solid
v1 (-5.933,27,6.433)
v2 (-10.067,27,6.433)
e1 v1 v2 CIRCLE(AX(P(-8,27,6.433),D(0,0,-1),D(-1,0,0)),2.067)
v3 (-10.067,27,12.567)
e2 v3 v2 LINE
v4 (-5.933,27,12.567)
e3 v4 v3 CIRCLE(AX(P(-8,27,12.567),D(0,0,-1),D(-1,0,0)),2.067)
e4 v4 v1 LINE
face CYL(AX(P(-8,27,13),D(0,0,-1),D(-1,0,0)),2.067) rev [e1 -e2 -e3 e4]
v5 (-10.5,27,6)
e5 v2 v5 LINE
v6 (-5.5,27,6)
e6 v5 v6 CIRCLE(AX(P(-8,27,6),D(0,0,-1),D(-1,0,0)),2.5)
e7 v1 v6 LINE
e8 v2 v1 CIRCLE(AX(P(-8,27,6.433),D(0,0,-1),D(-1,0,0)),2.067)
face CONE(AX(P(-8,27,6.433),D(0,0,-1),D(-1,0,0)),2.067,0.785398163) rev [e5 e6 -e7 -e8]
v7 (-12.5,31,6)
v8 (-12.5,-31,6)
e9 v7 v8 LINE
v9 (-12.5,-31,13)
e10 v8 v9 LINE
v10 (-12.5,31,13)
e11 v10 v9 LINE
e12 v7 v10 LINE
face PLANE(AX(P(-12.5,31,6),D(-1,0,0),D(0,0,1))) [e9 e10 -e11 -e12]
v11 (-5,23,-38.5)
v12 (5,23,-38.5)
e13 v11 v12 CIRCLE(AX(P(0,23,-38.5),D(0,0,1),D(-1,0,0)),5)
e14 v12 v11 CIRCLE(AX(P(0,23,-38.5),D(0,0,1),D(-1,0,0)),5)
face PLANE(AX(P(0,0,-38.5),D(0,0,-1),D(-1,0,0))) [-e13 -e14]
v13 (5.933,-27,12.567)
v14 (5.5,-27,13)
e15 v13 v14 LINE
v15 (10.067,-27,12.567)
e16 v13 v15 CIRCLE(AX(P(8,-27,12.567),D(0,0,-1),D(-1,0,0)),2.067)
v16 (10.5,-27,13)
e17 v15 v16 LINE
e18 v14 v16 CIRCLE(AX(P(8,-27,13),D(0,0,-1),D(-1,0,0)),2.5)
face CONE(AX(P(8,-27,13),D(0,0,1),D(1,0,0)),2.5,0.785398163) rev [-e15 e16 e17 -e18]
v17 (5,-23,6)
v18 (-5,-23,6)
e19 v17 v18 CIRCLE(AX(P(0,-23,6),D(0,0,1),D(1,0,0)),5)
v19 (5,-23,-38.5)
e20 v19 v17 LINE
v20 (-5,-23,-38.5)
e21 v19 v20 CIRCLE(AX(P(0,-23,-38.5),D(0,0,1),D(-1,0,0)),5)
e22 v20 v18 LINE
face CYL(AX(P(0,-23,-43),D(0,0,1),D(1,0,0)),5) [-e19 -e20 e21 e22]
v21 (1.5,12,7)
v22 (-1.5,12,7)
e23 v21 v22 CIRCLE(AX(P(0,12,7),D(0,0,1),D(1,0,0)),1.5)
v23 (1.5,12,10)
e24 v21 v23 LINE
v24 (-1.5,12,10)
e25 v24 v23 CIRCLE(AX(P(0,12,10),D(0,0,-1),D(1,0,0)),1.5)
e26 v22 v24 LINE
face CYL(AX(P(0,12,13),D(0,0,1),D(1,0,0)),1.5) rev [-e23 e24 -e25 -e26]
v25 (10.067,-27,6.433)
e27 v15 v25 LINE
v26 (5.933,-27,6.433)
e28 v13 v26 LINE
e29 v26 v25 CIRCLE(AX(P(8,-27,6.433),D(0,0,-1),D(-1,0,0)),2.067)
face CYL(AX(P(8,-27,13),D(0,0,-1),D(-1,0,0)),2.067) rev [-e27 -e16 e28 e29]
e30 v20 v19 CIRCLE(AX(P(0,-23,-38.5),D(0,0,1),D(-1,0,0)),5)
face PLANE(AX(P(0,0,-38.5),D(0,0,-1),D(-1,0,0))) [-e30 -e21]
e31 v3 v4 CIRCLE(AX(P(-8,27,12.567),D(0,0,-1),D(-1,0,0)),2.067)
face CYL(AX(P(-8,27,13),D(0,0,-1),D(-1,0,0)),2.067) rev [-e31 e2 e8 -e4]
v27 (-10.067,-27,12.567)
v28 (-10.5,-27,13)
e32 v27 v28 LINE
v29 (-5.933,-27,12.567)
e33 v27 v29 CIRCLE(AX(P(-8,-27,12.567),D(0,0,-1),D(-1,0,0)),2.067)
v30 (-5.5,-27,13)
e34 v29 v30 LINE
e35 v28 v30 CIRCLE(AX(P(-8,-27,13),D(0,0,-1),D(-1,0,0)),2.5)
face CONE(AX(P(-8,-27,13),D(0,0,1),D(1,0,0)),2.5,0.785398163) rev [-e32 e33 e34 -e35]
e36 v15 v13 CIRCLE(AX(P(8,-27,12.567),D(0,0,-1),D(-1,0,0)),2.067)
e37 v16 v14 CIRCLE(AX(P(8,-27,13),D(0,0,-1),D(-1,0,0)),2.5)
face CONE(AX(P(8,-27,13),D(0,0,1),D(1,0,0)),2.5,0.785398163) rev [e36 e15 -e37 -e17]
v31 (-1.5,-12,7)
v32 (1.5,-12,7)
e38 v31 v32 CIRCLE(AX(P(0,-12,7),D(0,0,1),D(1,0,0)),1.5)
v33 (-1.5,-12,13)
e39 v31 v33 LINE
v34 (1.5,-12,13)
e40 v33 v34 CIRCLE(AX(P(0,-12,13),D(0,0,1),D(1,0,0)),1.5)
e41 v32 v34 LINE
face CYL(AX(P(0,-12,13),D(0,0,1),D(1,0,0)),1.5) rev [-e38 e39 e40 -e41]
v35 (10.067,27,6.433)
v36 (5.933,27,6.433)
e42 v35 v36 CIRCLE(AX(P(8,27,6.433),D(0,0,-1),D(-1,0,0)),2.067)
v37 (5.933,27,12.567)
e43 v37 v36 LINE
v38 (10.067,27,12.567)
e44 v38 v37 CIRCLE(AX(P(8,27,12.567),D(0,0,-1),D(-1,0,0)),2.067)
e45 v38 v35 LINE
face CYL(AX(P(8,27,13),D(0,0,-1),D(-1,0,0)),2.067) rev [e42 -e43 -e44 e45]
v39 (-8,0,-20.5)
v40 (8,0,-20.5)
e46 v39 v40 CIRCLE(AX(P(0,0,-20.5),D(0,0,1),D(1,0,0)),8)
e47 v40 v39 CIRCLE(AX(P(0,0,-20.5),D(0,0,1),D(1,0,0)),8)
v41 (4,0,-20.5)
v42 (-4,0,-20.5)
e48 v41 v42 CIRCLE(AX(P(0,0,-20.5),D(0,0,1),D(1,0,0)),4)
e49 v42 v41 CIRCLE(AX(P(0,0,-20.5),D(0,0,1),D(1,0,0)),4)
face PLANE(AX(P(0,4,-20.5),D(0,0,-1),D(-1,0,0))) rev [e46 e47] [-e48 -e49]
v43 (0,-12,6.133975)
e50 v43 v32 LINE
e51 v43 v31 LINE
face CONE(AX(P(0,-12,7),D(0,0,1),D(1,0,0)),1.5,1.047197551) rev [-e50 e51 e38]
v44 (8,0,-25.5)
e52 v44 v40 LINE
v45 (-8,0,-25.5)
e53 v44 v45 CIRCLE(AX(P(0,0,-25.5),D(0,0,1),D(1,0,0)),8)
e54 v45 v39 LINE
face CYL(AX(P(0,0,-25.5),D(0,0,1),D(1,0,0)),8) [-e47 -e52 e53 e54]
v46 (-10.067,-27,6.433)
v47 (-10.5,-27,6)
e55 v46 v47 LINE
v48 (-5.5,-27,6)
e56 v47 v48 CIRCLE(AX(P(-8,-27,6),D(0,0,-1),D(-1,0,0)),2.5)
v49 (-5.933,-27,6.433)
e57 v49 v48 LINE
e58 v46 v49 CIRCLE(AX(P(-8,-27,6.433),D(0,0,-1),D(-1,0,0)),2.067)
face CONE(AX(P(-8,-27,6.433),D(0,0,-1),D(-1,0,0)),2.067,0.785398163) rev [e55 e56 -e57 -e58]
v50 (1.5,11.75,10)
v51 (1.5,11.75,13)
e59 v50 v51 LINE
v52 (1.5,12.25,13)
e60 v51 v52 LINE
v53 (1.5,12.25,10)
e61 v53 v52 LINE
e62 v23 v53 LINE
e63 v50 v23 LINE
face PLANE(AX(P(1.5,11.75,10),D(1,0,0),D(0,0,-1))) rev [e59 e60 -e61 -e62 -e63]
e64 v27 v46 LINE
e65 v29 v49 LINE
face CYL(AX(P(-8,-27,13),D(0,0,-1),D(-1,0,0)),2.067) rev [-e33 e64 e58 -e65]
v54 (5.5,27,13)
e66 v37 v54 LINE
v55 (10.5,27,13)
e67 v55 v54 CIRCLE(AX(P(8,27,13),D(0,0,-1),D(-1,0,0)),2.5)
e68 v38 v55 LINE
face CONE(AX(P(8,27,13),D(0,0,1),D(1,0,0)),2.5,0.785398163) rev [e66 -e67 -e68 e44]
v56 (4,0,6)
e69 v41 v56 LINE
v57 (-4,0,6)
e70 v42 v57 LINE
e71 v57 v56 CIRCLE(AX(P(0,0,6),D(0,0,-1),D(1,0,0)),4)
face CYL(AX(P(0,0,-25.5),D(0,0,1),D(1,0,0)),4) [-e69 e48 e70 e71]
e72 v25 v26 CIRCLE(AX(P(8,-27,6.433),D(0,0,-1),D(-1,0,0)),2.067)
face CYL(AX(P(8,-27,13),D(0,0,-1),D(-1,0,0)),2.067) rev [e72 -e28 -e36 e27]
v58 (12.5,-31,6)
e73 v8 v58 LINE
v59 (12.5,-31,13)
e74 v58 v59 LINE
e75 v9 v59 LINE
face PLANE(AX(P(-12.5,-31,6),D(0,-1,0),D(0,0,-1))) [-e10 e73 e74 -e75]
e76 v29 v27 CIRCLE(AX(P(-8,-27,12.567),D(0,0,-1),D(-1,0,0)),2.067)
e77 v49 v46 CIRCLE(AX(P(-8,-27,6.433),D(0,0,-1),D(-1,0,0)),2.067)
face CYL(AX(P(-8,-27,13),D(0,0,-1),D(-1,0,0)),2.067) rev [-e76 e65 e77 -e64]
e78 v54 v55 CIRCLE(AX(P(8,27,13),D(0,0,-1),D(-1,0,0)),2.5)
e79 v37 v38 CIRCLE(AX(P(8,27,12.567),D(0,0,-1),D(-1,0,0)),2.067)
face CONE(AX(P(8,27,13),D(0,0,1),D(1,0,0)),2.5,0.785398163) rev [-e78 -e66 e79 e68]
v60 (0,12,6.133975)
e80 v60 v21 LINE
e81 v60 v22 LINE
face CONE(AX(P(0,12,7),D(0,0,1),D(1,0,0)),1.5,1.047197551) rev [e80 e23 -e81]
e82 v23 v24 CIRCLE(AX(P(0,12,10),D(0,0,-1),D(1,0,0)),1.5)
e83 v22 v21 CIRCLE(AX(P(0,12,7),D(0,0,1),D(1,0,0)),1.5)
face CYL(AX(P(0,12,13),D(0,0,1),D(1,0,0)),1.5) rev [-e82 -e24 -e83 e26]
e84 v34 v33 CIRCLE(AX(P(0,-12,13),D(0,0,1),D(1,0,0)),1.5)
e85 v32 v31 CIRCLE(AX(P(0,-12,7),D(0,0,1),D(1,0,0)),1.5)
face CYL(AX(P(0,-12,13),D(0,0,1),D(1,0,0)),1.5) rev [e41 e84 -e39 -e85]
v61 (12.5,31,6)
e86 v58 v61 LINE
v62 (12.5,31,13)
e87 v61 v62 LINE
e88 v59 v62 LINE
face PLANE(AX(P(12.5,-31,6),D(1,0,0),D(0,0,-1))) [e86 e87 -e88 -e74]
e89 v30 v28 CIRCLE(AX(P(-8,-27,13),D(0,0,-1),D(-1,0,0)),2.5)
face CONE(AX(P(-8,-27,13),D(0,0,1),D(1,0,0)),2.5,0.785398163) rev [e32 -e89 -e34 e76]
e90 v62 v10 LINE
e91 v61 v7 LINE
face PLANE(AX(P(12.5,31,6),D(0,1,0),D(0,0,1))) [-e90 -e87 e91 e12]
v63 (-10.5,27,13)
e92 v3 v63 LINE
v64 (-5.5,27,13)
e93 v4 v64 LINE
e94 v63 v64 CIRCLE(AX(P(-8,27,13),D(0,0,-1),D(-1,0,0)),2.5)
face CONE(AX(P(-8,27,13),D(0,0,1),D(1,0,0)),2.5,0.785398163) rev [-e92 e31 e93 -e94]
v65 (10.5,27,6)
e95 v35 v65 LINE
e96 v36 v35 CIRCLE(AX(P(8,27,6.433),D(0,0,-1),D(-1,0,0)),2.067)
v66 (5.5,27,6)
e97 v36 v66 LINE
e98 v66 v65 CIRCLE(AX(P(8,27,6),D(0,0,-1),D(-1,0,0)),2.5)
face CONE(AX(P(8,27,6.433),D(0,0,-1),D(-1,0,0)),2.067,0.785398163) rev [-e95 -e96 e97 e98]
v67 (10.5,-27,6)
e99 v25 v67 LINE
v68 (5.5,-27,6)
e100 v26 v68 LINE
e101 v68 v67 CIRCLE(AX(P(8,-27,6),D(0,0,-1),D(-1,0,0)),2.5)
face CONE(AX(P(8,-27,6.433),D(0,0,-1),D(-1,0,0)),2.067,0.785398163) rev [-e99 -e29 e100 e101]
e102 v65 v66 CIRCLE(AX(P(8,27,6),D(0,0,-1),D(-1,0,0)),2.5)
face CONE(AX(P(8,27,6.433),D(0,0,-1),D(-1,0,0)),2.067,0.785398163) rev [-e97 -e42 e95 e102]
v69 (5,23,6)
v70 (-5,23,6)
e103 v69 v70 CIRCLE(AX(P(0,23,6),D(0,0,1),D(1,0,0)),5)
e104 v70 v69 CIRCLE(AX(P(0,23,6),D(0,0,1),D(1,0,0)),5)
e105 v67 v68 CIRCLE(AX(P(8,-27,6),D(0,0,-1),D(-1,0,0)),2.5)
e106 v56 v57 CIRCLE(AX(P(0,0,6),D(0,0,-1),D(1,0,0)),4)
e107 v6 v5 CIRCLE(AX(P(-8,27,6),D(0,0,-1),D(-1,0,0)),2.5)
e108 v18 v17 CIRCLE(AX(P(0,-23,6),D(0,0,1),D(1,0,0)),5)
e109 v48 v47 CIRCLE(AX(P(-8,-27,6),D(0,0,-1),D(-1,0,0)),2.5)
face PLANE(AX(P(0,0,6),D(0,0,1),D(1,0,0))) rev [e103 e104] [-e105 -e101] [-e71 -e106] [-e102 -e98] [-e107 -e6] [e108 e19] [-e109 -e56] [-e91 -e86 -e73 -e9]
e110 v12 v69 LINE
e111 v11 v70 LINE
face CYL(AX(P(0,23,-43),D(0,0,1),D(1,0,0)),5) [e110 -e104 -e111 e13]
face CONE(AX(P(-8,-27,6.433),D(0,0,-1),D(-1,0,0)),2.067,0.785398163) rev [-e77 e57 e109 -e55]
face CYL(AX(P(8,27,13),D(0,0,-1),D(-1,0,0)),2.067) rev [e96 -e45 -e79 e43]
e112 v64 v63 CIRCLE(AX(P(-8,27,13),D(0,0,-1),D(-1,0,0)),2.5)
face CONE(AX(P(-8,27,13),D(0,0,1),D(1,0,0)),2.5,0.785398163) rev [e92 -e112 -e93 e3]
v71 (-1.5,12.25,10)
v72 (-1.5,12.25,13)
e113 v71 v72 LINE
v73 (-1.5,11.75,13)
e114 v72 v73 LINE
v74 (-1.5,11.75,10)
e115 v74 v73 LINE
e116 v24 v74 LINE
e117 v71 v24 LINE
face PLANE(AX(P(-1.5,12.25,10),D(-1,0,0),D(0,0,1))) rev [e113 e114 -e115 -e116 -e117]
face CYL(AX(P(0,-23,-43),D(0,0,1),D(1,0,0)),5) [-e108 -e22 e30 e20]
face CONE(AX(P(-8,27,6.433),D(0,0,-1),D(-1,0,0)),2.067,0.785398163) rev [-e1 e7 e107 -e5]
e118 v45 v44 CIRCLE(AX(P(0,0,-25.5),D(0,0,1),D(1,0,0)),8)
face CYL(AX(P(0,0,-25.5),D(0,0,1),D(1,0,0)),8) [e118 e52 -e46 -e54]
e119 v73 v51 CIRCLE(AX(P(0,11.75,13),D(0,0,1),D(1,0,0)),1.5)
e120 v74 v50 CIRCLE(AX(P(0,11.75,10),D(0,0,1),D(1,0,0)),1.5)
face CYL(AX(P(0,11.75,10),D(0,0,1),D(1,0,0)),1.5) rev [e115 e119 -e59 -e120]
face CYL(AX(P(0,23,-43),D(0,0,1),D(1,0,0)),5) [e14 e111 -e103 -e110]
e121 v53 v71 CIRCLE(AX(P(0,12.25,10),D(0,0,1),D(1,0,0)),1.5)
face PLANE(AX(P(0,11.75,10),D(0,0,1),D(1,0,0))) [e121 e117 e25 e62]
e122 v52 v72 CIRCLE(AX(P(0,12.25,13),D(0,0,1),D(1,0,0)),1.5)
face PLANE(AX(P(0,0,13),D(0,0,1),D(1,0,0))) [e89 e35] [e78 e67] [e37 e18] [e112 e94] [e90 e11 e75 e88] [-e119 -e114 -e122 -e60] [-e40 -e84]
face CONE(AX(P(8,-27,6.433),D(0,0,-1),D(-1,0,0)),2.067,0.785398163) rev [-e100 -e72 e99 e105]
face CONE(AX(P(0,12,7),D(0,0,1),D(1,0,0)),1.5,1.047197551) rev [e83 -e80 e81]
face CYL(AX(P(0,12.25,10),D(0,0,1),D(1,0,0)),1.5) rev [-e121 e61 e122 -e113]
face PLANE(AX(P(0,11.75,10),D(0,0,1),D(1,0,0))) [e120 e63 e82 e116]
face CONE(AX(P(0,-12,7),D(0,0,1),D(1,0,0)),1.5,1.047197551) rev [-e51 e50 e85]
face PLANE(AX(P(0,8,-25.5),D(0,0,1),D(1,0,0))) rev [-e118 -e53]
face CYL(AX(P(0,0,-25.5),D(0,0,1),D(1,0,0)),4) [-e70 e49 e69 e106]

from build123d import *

# Parameters (mm, degrees)
SKETCH1_W           = 25
SKETCH1_H           = 62
BOSS_EXTRUDE1_DEPTH = 7
SKETCH2_R           = 5
BOSS_EXTRUDE2_DEPTH = 56
SKETCH3_R           = 5
BOSS_EXTRUDE3_DEPTH = 56
HOLE1_D             = 3
HOLE1_DEPTH         = 6
HOLE1_TIP           = 0.866025404
CUT_EXTRUDE1_DEPTH  = 3
HOLE2_D             = 3
HOLE2_DEPTH         = 6
HOLE2_TIP           = 0.866025404
SKETCH14_W          = 10
SKETCH14_H          = 56
CUT_EXTRUDE2_DEPTH  = 4.5


with BuildPart() as part:
    # Sketch1 → Boss-Extrude1 (new body)
    with BuildSketch(Plane.XY.offset(13)):
        Rectangle(SKETCH1_W, SKETCH1_H)
    extrude(amount=-BOSS_EXTRUDE1_DEPTH)

    # Sketch2 → Boss-Extrude2 (add)
    with BuildSketch(Plane.XY.offset(13)):
        with Locations((0, 23)):
            Circle(SKETCH2_R)
    extrude(amount=-BOSS_EXTRUDE2_DEPTH)

    # Sketch3 → Boss-Extrude3 (add)
    with BuildSketch(Plane.XY.offset(13)):
        with Locations((0, -23)):
            Circle(SKETCH3_R)
    extrude(amount=-BOSS_EXTRUDE3_DEPTH)

    # Sketch4 → Revolve1 (revolve)
    with BuildSketch(Plane(origin=(0, 0, 0), x_dir=(0, 0, -1), z_dir=(1, 0, 0)), mode=Mode.PRIVATE) as revolve1_sk:
        Polygon((-6, 0), (-6, 4), (20.5, 4), (20.5, 8), (25.5, 8), (25.5, 0), align=None)
    revolve(revolve1_sk.sketch.rotate(Axis((0, 0, -25.5), (0, 0, 1)), 270), axis=Axis((0, 0, -25.5), (0, 0, 1)))

    # Hole1
    with Locations(Plane.XY.offset(13)):
        with Locations((0, 12)):
            Hole(HOLE1_D / 2, depth=HOLE1_DEPTH)
            with Locations((0, 0, -(HOLE1_DEPTH + HOLE1_TIP / 2))):  # 120° drill point
                Cone(0, HOLE1_D / 2, HOLE1_TIP, mode=Mode.SUBTRACT)

    # Sketch7 → Cut-Extrude1 (cut)
    with BuildSketch(Plane.XY.offset(13)):
        with BuildLine():
            Line((1.5, 11.75), (1.5, 12.25))
            ThreePointArc((1.5, 12.25), (0, 13.75), (-1.5, 12.25))
            Line((-1.5, 12.25), (-1.5, 11.75))
            ThreePointArc((-1.5, 11.75), (0, 10.25), (1.5, 11.75))
        make_face()
    extrude(amount=-CUT_EXTRUDE1_DEPTH, mode=Mode.SUBTRACT)

    # Hole2
    with Locations(Plane.XY.offset(13)):
        with Locations((0, -12)):
            Hole(HOLE2_D / 2, depth=HOLE2_DEPTH)
            with Locations((0, 0, -(HOLE2_DEPTH + HOLE2_TIP / 2))):  # 120° drill point
                Cone(0, HOLE2_D / 2, HOLE2_TIP, mode=Mode.SUBTRACT)

    # Sketch10 → Cut-Revolve1 (revolve, cut)
    with BuildSketch(Plane(origin=(0, -27, 0), x_dir=(1, 0, 0), z_dir=(0, 1, 0)), mode=Mode.PRIVATE) as cut_revolve1_sk:
        Polygon((8, -6), (10.5, -6), (10.067, -6.433), (10.067, -12.567), (10.5, -13), (8, -13), align=None)
    revolve(cut_revolve1_sk.sketch.rotate(Axis((8, -27, 13), (0, 0, -1)), 180), axis=Axis((8, -27, 13), (0, 0, -1)), mode=Mode.SUBTRACT)

    # Sketch11 → Cut-Revolve2 (revolve, cut)
    with BuildSketch(Plane(origin=(0, -27, 0), x_dir=(1, 0, 0), z_dir=(0, 1, 0)), mode=Mode.PRIVATE) as cut_revolve2_sk:
        Polygon((-8, -6), (-5.5, -6), (-5.933, -6.433), (-5.933, -12.567), (-5.5, -13), (-8, -13), align=None)
    revolve(cut_revolve2_sk.sketch.rotate(Axis((-8, -27, 13), (0, 0, -1)), 180), axis=Axis((-8, -27, 13), (0, 0, -1)), mode=Mode.SUBTRACT)

    # Sketch12 → Cut-Revolve3 (revolve, cut)
    with BuildSketch(Plane(origin=(0, 27, 0), x_dir=(1, 0, 0), z_dir=(0, 1, 0)), mode=Mode.PRIVATE) as cut_revolve3_sk:
        Polygon((8, -6), (10.5, -6), (10.067, -6.433), (10.067, -12.567), (10.5, -13), (8, -13), align=None)
    revolve(cut_revolve3_sk.sketch.rotate(Axis((8, 27, 13), (0, 0, -1)), 180), axis=Axis((8, 27, 13), (0, 0, -1)), mode=Mode.SUBTRACT)

    # Sketch13 → Cut-Revolve4 (revolve, cut)
    with BuildSketch(Plane(origin=(0, 27, 0), x_dir=(1, 0, 0), z_dir=(0, 1, 0)), mode=Mode.PRIVATE) as cut_revolve4_sk:
        Polygon((-8, -6), (-5.5, -6), (-5.933, -6.433), (-5.933, -12.567), (-5.5, -13), (-8, -13), align=None)
    revolve(cut_revolve4_sk.sketch.rotate(Axis((-8, 27, 13), (0, 0, -1)), 180), axis=Axis((-8, 27, 13), (0, 0, -1)), mode=Mode.SUBTRACT)

    # Sketch14 → Cut-Extrude2 (cut)
    with BuildSketch(Plane(origin=(0, 0, -43), x_dir=(-1, 0, 0), z_dir=(0, 0, -1))):
        Rectangle(SKETCH14_W, SKETCH14_H)
    extrude(amount=-CUT_EXTRUDE2_DEPTH, mode=Mode.SUBTRACT)


solid = part.part
